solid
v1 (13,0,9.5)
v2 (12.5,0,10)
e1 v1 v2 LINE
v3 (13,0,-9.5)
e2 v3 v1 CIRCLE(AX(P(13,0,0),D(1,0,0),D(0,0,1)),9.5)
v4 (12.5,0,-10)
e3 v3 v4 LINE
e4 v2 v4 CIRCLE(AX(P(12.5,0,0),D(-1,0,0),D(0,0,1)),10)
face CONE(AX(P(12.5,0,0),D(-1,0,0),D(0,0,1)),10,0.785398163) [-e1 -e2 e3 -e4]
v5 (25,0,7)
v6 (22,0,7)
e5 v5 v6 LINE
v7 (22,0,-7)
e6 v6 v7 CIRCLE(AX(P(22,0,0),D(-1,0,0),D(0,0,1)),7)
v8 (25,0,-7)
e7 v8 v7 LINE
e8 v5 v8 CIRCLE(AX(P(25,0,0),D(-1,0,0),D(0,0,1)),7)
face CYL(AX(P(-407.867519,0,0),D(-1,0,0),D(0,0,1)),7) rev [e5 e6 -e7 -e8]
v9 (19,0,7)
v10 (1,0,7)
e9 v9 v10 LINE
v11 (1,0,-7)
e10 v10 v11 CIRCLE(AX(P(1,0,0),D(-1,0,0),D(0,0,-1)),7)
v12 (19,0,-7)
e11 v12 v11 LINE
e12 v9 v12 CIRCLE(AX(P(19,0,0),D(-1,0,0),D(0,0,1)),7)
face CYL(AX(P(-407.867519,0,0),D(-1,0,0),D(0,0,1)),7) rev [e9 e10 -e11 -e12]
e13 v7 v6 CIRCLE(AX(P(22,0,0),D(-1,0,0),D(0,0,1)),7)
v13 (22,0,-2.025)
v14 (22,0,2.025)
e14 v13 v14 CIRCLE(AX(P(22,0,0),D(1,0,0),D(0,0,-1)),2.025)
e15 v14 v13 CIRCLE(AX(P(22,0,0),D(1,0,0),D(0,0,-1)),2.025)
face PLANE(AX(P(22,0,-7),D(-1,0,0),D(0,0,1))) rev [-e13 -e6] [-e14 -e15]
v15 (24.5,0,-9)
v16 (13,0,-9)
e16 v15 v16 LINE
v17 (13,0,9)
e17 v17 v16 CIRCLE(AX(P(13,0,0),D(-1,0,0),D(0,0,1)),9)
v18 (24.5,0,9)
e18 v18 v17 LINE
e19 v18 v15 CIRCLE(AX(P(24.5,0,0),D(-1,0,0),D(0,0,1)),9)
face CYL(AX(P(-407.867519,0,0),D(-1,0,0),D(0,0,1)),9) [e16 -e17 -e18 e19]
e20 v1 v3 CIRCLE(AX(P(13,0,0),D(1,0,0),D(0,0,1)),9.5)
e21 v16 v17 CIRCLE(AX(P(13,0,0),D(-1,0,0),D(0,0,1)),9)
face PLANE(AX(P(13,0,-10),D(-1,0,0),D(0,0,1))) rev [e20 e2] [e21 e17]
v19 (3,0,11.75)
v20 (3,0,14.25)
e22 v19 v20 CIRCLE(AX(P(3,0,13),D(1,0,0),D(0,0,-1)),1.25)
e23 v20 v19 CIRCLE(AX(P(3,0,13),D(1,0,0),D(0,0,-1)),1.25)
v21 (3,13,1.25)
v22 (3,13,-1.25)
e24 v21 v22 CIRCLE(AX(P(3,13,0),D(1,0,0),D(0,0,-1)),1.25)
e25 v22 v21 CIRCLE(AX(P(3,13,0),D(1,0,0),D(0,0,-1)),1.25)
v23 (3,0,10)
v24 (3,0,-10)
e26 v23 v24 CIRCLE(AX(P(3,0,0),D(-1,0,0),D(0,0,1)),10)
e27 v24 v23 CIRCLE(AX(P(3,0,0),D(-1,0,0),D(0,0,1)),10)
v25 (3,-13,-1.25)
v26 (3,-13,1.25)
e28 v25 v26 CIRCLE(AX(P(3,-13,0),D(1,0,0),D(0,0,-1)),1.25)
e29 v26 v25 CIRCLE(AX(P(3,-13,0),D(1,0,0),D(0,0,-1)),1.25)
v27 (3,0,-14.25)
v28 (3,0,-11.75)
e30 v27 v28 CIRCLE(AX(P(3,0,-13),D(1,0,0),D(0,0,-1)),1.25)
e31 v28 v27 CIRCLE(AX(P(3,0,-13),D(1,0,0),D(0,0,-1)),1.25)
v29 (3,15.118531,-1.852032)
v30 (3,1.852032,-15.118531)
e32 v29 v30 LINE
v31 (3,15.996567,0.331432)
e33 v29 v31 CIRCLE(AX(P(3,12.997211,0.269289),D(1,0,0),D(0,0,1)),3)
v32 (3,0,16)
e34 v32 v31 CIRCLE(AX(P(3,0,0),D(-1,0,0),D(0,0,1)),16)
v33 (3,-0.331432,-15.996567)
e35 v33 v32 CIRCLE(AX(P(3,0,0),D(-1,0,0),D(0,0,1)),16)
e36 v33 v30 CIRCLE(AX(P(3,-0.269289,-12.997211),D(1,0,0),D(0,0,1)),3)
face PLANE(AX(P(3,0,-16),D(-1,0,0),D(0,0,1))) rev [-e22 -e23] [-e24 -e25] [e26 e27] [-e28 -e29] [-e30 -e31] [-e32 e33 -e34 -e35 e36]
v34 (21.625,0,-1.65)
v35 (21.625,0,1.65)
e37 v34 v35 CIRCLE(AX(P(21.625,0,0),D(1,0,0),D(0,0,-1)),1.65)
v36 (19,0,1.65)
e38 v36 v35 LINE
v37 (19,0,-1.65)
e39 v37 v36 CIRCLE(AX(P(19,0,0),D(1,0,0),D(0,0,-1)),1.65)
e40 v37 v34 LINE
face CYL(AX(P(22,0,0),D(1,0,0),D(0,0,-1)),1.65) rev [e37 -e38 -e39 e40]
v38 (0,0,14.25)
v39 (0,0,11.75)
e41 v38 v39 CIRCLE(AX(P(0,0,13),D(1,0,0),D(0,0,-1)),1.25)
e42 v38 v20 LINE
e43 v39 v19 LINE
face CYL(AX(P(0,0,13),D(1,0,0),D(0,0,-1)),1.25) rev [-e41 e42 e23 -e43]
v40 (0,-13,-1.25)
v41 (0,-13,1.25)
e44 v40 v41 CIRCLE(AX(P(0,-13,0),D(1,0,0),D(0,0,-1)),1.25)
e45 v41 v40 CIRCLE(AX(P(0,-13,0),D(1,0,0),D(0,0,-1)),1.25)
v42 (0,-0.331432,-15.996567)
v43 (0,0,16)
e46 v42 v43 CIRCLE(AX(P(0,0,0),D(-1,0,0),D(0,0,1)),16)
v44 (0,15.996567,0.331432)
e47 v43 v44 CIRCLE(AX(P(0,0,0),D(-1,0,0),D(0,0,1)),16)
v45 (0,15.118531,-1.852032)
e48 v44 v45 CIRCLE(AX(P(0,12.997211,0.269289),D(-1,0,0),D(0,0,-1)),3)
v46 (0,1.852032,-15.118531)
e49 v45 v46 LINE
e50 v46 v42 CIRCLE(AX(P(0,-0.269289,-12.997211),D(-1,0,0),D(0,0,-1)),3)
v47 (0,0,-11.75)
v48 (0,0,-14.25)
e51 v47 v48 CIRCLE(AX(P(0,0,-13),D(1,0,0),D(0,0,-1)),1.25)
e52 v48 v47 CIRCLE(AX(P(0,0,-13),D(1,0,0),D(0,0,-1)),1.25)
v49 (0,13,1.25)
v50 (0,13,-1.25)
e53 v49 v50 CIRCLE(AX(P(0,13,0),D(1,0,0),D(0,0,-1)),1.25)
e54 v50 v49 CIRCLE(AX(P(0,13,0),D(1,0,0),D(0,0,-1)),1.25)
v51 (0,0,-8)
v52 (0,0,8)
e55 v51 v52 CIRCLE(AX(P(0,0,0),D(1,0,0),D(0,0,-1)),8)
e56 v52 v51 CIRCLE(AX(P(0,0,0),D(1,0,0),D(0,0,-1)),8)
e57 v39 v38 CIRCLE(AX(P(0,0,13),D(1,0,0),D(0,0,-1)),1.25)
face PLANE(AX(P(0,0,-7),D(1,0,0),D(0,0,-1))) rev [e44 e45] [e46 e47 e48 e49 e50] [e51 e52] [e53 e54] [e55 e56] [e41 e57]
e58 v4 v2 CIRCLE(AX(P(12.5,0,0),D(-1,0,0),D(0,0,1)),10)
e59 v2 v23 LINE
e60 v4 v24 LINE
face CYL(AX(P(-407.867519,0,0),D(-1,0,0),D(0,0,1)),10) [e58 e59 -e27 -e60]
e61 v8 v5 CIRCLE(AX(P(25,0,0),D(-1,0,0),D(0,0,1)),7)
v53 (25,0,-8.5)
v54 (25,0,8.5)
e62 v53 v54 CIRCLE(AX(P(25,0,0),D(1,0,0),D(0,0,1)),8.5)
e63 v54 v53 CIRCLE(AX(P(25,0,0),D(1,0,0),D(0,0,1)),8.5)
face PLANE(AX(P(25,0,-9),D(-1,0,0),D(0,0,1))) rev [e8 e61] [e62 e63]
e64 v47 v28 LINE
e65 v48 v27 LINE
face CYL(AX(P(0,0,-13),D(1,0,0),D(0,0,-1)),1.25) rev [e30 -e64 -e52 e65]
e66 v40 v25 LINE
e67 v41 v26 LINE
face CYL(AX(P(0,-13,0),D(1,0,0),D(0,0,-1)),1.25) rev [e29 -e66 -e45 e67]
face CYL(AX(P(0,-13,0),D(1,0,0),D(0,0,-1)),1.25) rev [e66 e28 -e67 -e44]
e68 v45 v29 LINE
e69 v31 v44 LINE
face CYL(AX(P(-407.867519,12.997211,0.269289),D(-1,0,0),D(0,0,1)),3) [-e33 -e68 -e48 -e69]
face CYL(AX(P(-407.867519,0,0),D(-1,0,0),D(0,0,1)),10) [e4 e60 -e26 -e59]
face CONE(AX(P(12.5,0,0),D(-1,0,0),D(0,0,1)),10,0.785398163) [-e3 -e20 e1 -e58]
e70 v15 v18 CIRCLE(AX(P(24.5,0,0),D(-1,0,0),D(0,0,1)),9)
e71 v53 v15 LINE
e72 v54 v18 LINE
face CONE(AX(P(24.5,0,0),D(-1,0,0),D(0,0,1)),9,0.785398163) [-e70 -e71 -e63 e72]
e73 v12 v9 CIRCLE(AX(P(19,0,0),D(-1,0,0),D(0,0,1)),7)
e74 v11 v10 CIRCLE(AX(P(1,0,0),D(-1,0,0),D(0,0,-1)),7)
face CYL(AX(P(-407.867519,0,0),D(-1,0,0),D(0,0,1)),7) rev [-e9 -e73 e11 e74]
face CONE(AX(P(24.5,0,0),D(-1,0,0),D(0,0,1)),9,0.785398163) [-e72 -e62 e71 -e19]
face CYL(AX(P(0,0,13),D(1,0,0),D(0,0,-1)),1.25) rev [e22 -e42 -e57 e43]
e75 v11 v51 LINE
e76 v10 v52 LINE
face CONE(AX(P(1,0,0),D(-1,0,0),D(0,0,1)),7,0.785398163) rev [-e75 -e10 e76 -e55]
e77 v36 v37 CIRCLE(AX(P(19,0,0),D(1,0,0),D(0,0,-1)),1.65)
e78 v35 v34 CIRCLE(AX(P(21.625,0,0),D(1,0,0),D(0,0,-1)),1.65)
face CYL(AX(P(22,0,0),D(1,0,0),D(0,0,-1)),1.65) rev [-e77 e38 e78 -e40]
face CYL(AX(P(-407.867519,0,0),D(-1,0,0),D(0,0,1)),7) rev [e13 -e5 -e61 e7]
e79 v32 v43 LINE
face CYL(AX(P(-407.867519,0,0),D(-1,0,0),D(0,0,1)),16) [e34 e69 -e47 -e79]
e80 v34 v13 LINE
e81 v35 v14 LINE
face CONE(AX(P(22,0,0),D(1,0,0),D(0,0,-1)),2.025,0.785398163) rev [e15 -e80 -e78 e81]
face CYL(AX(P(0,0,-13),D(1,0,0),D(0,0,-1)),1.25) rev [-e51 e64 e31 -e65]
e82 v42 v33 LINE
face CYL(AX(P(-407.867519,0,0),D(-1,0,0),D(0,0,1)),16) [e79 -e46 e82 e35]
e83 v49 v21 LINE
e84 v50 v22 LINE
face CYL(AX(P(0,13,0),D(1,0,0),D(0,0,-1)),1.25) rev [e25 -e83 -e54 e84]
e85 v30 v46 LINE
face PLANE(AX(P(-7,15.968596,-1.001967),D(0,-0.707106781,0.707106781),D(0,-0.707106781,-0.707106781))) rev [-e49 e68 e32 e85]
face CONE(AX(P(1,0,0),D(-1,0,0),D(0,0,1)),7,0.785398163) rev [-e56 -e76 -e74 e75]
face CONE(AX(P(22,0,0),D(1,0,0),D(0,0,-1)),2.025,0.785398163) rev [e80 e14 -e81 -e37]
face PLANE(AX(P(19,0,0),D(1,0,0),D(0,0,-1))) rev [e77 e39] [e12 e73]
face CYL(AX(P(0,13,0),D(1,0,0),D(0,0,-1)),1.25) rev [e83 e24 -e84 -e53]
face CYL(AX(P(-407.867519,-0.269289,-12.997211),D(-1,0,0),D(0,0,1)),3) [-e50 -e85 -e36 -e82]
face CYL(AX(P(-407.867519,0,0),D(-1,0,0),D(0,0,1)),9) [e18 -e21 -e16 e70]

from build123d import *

# Parameters (mm, degrees)
SKETCH_2_R                   = 1.25
CUT_EXTRUDE_1_DEPTH          = 32.559467676
HOLE_WIZARD_M4_1_D           = 3.3
HOLE_WIZARD_M4_1_CSINK_D     = 4.05
HOLE_WIZARD_M4_1_CSINK_ANGLE = 90
CHAMFER_1_SIZE               = 0.5
CHAMFER_2_SIZE               = 1
CUT_EXTRUDE_2_DEPTH          = 10
FILLET_1_R                   = 3
HOLE_WIZARD_M3_1_D           = 2.5


with BuildPart() as part:
    # 草图1 → 旋转1 (revolve)
    with BuildSketch(Plane(origin=(0, 0, 0), x_dir=(1, 0, 0), z_dir=(0, 1, 0)), mode=Mode.PRIVATE) as revolve_1_sk:
        Polygon((0, 7), (0, 16), (3, 16), (3, 10), (13, 10), (13, 9), (25, 9), (25, 7), (22, 7), (22, 0), (19, 0), (19, 7), align=None)
    revolve(revolve_1_sk.sketch.rotate(Axis((-407.867518885, 0, 0), (1, 0, 0)), 180), axis=Axis((-407.867518885, 0, 0), (1, 0, 0)))

    # 草图2 → 切除-拉伸1 (cut, through all)
    with BuildSketch(Plane(origin=(3, 0, 0), x_dir=(0, 0, -1), z_dir=(1, 0, 0))):
        with Locations((0, 13)):
            Circle(SKETCH_2_R)
        with Locations((13, 0)):
            Circle(SKETCH_2_R)
        with Locations((0, -13)):
            Circle(SKETCH_2_R)
        with Locations((-13, 0)):
            Circle(SKETCH_2_R)
    extrude(amount=-CUT_EXTRUDE_1_DEPTH, mode=Mode.SUBTRACT)

    # M4 螺纹孔1 (through all)
    with Locations(Plane(origin=(22, 0, 0), x_dir=(0, 0, -1), z_dir=(1, 0, 0))):
        with Locations((0, 0)):
            CounterSinkHole(HOLE_WIZARD_M4_1_D / 2, HOLE_WIZARD_M4_1_CSINK_D / 2, counter_sink_angle=HOLE_WIZARD_M4_1_CSINK_ANGLE)

    # 倒角1
    chamfer_1_edges = [part.edges().sort_by_distance(p)[0] for p in [
        (25, 0, -9),
        (13, 0, -10),
    ]]
    chamfer(chamfer_1_edges, length=CHAMFER_1_SIZE)

    # 倒角2
    chamfer_2_edges = [part.edges().sort_by_distance(p)[0] for p in [
        (0, 0, -7),
    ]]
    chamfer(chamfer_2_edges, length=CHAMFER_2_SIZE)

    # 草图5 → 切除-拉伸2 (cut)
    with BuildSketch(Plane(origin=(3, 0, 0), x_dir=(0, 0, -1), z_dir=(1, 0, 0))):
        with BuildLine():
            Line((1.001966601, 15.968596148), (15.968596148, 1.001966601))
            ThreePointArc((15.968596148, 1.001966601), (11.313708499, 11.313708499), (1.001966601, 15.968596148))
        make_face()
    extrude(amount=-CUT_EXTRUDE_2_DEPTH, mode=Mode.SUBTRACT)

    # 圆角1
    fillet_1_edges = [part.edges().sort_by_distance(p)[0] for p in [
        (1.5, 15.968596148, -1.001966601),
        (1.5, 1.001966601, -15.968596148),
    ]]
    fillet(fillet_1_edges, radius=FILLET_1_R)

    # M3 螺纹孔1 (through all)
    with Locations(Plane(origin=(3, 13, 0), x_dir=(0, 0, 1), z_dir=(1, 0, 0))):
        with Locations((0, 0), (13, 13), (0, 26), (-13, 13)):
            Hole(HOLE_WIZARD_M3_1_D / 2)


solid = part.part
